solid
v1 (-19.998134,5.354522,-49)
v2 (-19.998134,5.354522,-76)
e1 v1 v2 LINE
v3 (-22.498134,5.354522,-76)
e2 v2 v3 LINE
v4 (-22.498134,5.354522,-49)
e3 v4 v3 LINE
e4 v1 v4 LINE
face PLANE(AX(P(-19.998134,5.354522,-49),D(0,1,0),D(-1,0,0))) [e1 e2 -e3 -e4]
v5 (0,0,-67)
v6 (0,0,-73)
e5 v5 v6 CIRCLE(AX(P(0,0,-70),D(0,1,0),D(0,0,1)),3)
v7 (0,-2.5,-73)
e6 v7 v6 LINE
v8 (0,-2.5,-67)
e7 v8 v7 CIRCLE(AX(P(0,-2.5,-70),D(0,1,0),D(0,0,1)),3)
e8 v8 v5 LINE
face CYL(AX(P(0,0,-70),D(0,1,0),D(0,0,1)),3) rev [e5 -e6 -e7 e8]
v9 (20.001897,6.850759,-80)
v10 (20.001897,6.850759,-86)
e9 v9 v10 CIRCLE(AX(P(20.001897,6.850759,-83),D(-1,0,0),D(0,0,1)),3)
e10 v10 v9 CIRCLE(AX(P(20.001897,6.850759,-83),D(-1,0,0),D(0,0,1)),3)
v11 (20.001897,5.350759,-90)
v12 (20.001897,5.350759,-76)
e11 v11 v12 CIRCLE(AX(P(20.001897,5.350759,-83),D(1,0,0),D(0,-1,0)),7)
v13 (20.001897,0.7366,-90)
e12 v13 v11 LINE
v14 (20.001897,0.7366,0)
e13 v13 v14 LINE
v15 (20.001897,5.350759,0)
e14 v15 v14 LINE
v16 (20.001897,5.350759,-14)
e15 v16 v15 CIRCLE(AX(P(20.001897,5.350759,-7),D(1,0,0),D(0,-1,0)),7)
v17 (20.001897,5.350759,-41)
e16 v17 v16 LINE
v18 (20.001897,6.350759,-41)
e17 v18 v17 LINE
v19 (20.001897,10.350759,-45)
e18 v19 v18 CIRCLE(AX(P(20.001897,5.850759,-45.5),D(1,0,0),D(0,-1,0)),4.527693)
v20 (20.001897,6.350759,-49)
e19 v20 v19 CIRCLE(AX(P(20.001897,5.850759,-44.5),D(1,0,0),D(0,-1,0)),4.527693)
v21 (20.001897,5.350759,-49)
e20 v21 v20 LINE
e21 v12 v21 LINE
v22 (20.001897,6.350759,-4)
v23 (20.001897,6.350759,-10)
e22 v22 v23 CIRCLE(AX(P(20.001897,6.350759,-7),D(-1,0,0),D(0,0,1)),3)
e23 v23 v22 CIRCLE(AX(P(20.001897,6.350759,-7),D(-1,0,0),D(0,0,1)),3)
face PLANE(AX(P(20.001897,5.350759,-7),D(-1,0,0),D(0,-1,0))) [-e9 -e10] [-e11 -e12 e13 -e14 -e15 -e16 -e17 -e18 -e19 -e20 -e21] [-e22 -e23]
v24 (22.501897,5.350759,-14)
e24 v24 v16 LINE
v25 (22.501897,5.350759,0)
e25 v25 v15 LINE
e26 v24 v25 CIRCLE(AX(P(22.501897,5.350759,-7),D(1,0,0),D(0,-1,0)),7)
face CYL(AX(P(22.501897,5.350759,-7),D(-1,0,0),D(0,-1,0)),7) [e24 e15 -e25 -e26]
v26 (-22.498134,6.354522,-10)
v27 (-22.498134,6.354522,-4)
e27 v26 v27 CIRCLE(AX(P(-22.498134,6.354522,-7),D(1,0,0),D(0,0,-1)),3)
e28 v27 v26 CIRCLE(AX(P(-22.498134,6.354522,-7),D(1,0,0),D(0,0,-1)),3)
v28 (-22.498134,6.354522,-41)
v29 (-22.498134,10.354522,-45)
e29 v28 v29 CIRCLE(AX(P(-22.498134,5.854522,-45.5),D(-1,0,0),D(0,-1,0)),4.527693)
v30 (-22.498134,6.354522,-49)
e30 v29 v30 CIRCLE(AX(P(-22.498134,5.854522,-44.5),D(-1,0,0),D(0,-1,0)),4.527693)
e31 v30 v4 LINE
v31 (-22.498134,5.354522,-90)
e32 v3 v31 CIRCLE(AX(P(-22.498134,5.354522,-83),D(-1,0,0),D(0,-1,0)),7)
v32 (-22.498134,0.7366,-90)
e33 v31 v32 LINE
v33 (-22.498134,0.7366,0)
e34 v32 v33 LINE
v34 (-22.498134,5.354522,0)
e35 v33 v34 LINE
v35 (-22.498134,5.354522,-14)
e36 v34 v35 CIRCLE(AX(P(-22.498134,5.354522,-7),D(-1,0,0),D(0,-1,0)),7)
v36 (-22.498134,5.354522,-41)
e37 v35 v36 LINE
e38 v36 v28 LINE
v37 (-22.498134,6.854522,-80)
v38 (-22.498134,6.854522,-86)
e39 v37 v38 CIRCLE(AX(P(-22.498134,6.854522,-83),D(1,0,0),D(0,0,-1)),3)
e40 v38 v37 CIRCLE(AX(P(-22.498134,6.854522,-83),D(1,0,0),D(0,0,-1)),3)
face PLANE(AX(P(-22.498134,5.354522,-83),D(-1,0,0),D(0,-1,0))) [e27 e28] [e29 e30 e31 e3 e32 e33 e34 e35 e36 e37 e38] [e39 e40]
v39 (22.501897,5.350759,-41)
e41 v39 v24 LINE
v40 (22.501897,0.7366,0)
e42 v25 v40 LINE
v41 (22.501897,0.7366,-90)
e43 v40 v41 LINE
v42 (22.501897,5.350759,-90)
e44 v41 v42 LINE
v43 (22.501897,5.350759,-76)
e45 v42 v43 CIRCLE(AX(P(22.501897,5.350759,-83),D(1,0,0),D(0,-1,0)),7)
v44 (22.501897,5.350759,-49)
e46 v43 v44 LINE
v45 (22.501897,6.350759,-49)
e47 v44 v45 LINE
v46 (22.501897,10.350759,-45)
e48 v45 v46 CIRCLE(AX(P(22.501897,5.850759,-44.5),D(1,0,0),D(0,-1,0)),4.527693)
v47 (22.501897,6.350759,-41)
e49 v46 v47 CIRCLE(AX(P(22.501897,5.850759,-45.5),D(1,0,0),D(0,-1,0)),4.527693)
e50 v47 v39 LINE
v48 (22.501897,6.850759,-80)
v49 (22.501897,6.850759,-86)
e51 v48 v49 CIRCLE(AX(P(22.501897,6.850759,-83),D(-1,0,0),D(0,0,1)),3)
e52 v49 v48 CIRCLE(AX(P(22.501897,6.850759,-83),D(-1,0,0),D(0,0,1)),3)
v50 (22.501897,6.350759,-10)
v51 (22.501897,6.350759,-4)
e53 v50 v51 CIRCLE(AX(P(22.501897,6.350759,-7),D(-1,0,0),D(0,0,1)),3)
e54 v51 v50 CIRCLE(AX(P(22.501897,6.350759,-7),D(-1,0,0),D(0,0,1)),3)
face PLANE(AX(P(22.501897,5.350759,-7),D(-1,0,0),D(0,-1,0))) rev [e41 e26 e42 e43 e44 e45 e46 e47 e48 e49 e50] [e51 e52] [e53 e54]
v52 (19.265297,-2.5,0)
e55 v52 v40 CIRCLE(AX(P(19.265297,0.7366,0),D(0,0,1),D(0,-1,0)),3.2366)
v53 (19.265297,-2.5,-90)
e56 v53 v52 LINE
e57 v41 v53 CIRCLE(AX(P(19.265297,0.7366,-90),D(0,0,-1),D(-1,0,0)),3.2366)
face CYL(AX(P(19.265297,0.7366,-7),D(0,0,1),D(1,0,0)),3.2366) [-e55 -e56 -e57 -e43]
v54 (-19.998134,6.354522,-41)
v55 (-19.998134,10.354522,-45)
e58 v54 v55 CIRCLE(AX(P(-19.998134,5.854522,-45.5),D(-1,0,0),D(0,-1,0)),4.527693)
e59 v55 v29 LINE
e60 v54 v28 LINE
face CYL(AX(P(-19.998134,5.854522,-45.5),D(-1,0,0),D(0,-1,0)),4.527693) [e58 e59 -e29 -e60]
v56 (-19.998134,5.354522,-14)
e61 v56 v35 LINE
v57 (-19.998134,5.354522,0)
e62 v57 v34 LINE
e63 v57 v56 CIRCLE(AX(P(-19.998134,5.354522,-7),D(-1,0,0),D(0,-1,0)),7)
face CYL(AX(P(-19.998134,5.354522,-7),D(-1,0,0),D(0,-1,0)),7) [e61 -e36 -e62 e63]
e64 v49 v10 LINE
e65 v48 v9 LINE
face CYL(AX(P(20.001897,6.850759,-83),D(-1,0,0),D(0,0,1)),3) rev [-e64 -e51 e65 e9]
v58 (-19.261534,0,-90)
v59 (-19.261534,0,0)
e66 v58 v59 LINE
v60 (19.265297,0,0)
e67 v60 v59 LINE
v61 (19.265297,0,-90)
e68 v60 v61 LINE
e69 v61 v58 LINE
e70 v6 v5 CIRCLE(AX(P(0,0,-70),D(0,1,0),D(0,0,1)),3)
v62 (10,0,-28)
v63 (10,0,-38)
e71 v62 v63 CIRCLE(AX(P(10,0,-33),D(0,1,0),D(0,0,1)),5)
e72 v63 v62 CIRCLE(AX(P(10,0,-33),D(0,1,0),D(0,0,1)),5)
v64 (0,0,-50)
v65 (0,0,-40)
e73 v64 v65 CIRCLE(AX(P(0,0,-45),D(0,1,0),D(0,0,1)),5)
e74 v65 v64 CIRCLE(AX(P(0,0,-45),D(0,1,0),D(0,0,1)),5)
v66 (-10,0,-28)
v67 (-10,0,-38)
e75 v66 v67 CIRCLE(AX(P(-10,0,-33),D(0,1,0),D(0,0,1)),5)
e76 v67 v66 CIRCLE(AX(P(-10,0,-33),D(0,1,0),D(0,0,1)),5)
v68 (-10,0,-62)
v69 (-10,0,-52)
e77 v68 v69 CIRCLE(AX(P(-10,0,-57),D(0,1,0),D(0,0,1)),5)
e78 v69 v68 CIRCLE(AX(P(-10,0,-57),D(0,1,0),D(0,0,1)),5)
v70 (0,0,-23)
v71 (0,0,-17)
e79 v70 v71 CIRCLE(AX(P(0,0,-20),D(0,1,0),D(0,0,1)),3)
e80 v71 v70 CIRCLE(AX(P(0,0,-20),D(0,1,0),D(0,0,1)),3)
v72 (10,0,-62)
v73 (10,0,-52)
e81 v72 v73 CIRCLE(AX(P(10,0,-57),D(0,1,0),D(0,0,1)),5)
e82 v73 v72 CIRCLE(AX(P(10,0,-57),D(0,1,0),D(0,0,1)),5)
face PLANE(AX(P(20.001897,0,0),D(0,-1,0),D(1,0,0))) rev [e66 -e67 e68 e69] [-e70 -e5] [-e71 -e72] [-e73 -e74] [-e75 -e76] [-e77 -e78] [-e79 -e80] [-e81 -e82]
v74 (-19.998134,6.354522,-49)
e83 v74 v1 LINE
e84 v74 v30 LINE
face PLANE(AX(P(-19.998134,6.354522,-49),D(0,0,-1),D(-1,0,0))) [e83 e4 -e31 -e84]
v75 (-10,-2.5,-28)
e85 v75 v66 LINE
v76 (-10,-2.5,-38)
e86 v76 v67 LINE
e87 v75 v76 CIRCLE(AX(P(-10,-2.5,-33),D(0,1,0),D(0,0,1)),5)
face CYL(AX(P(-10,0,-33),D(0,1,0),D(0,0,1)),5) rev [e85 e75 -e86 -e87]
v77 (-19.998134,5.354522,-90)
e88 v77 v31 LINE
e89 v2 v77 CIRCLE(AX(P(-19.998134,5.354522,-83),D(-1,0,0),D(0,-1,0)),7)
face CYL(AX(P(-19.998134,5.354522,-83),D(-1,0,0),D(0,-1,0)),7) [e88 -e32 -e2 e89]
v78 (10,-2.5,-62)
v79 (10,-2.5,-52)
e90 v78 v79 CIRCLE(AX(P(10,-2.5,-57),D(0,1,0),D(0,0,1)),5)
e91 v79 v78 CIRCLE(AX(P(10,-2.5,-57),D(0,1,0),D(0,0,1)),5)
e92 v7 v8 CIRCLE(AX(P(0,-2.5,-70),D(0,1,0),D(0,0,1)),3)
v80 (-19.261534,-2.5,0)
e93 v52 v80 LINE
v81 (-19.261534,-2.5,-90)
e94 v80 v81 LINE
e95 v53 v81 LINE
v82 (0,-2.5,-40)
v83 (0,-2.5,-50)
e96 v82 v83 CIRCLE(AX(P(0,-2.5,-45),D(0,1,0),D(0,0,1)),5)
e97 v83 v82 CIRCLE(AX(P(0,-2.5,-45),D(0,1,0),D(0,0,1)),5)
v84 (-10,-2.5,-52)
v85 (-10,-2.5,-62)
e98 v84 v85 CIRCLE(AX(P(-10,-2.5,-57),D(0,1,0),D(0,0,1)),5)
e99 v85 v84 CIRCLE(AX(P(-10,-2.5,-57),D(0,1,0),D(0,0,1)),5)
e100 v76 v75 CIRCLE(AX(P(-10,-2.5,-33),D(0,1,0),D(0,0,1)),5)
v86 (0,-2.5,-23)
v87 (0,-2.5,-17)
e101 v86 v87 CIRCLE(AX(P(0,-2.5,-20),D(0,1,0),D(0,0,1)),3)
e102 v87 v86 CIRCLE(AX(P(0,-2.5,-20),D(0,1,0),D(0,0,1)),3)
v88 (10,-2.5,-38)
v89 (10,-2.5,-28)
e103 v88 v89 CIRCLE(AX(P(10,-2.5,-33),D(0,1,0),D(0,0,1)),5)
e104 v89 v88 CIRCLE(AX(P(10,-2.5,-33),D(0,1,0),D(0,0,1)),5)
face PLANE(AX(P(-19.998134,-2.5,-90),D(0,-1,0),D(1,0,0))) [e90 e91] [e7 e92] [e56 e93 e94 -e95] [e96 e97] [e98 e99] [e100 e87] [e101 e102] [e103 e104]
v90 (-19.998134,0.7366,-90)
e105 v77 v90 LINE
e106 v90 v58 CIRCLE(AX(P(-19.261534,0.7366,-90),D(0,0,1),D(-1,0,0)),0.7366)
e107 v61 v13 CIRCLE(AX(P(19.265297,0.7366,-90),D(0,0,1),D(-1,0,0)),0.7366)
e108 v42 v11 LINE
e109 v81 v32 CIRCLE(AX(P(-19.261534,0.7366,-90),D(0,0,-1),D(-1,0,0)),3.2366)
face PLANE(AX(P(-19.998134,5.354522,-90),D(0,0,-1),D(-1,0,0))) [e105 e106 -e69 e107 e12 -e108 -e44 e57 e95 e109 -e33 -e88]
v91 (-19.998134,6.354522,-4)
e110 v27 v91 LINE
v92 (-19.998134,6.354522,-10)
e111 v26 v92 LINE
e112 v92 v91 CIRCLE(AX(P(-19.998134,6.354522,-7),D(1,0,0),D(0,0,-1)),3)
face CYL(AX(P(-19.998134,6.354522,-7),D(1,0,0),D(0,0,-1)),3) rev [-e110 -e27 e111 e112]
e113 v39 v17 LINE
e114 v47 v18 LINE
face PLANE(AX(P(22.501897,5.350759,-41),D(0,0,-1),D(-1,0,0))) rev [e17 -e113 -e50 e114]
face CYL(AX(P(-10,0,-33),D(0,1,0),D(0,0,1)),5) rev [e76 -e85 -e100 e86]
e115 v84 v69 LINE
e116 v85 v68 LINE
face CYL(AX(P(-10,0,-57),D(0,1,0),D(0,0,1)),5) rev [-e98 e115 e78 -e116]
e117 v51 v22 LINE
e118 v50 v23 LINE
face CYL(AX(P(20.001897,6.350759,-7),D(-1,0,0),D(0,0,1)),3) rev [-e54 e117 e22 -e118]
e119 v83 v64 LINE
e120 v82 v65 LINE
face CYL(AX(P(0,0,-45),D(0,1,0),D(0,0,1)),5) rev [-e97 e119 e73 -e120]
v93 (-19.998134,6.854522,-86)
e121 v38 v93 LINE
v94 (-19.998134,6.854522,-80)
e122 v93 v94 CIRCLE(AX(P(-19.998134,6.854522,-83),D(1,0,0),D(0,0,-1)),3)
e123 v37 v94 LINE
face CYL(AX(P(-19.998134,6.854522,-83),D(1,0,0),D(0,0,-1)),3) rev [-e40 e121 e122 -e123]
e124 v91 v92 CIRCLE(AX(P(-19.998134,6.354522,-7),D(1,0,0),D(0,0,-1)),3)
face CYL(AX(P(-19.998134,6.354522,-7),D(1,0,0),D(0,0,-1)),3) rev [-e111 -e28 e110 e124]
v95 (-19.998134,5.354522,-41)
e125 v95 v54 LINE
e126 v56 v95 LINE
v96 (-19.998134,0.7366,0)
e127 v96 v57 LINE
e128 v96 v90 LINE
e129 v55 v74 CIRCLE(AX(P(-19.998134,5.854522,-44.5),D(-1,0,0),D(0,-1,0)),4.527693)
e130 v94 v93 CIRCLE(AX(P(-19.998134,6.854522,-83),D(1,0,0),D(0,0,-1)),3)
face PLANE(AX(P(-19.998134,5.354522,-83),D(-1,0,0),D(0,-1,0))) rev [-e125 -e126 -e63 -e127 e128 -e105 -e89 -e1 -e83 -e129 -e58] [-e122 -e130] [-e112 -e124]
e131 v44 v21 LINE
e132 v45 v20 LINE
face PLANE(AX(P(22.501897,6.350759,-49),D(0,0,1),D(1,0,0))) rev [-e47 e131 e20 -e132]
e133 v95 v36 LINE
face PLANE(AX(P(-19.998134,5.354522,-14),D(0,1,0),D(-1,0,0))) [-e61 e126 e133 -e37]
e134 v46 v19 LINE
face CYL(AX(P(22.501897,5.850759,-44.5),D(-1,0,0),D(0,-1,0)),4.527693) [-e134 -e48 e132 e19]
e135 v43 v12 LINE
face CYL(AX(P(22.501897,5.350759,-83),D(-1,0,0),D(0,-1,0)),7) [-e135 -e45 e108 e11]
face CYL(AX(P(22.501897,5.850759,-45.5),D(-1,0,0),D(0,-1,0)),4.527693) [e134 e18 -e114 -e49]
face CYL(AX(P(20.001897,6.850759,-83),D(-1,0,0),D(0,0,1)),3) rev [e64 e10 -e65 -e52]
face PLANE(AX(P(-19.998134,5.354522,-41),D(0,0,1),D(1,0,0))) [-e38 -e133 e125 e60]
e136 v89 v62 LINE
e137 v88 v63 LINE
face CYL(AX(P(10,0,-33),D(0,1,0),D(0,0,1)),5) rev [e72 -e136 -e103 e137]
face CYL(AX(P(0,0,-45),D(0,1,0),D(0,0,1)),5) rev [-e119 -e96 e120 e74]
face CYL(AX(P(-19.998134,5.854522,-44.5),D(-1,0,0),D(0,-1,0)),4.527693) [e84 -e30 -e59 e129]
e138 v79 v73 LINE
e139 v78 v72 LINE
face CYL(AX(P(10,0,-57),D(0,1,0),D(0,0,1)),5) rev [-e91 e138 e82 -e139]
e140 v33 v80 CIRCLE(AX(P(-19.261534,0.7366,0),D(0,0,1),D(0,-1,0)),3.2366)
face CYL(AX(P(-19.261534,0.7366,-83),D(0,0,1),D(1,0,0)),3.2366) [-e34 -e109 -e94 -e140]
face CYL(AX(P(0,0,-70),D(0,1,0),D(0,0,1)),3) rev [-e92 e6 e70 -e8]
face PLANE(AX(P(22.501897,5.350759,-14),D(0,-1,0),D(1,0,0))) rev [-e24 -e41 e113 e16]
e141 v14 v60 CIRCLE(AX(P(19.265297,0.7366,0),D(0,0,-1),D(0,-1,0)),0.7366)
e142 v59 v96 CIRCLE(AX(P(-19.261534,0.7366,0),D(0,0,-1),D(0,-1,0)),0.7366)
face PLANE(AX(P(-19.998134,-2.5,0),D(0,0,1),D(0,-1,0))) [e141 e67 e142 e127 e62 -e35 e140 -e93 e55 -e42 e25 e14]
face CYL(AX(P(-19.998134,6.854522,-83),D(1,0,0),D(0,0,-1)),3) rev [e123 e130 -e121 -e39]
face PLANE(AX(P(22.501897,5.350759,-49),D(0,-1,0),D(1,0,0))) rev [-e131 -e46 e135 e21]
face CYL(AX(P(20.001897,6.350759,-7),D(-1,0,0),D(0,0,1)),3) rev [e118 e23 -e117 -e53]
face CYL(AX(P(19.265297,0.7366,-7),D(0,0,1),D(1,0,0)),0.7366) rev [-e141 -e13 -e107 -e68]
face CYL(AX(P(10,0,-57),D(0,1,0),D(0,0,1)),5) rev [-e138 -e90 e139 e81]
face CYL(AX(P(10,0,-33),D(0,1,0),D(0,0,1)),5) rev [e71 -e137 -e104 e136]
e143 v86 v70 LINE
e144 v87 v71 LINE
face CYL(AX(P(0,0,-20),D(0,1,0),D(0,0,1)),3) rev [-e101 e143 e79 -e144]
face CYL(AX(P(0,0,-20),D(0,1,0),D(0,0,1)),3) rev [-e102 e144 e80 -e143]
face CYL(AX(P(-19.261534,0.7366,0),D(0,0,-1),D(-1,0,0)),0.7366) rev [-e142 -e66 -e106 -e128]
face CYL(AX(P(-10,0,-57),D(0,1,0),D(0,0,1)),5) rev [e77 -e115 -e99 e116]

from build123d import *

# Parameters (mm, degrees)
BOSS_EXTRUDE1_DEPTH          = 2.5
SKETCH2_W                    = 90
SKETCH2_H                    = 2.5
BOSS_EXTRUDE2_DEPTH          = 40.000031182
BOSS_EXTRUDE3_DEPTH          = 2.5
F_6_0_6_DIAMETER_HOLE1_D     = 6
F_6_0_6_DIAMETER_HOLE1_DEPTH = 2.5
F_6_0_6_DIAMETER_HOLE2_D     = 6
F_6_0_6_DIAMETER_HOLE2_DEPTH = 2.5
F_10_0_10_DIAMETER_HOLE1_D   = 10
F_6_0_6_DIAMETER_HOLE3_D     = 6
FILLET1_R                    = 0.7366
FILLET2_R                    = 3.2366


with BuildPart() as part:
    # Sketch1 → Boss-Extrude1 (new body)
    with BuildSketch(Plane(origin=(-22.498134156, 0, 0), x_dir=(0, -1, 0), z_dir=(-1, 0, 0))):
        with BuildLine():
            Line((-5.354521861, -90), (2.5, -90))
            Line((2.5, -90), (2.5, 0))
            Line((2.5, 0), (-5.354521861, 0))
            ThreePointArc((-5.354521861, 0), (-12.354521861, -7), (-5.354521861, -14))
            Line((-5.354521861, -14), (-5.354521861, -41))
            Line((-5.354521861, -41), (-6.354521861, -41))
            ThreePointArc((-6.354521861, -41), (-9.05608398, -42.298437881), (-10.354521861, -45))
            ThreePointArc((-10.354521861, -45), (-9.05608398, -47.701562119), (-6.354521861, -49))
            Line((-6.354521861, -49), (-5.354521861, -49))
            Line((-5.354521861, -49), (-5.354521861, -76))
            ThreePointArc((-5.354521861, -76), (-12.354521861, -83), (-5.354521861, -90))
        make_face()
    extrude(amount=-BOSS_EXTRUDE1_DEPTH)

    # Sketch2 → Boss-Extrude2 (add)
    with BuildSketch(Plane(origin=(-19.998134156, 0, 0), x_dir=(0, 0, -1), z_dir=(1, 0, 0))):
        with Locations((45, -1.25)):
            Rectangle(SKETCH2_W, SKETCH2_H)
    extrude(amount=BOSS_EXTRUDE2_DEPTH)

    # Sketch3 → Boss-Extrude3 (add)
    with BuildSketch(Plane(origin=(20.001897026, 0, 0), x_dir=(0, 0, -1), z_dir=(1, 0, 0))):
        with BuildLine():
            Line((0, -2.5), (0, 5.350758991))
            ThreePointArc((0, 5.350758991), (7, 12.350758991), (14, 5.350758991))
            Line((14, 5.350758991), (41, 5.350758991))
            Line((41, 5.350758991), (41, 6.350758991))
            ThreePointArc((41, 6.350758991), (42.298437881, 9.05232111), (45, 10.350758991))
            ThreePointArc((45, 10.350758991), (47.701562119, 9.05232111), (49, 6.350758991))
            Line((49, 6.350758991), (49, 5.350758991))
            Line((49, 5.350758991), (76, 5.350758991))
            ThreePointArc((76, 5.350758991), (83, 12.350758991), (90, 5.350758991))
            Line((90, 5.350758991), (90, -2.5))
            Line((90, -2.5), (0, -2.5))
        make_face()
    extrude(amount=BOSS_EXTRUDE3_DEPTH)

    # Ø6.0 (6) Diameter Hole1
    with Locations(Plane.ZY.offset(-20.001897026)):
        with Locations((-83, 6.850758991), (-7, 6.350758991)):
            Hole(F_6_0_6_DIAMETER_HOLE1_D / 2, depth=F_6_0_6_DIAMETER_HOLE1_DEPTH)

    # Ø6.0 (6) Diameter Hole2
    with Locations(Plane(origin=(-19.998134156, 0, 0), x_dir=(0, 0, -1), z_dir=(1, 0, 0))):
        with Locations((83, 6.854521861), (7, 6.354521861)):
            Hole(F_6_0_6_DIAMETER_HOLE2_D / 2, depth=F_6_0_6_DIAMETER_HOLE2_DEPTH)

    # Ø10.0 (10) Diameter Hole1 (through all)
    with Locations(Plane(origin=(0, 0, 0), x_dir=(1, 0, 0), z_dir=(0, 1, 0))):
        with Locations((0, 45), (-10, 57), (-10, 33), (10, 33), (10, 57)):
            Hole(F_10_0_10_DIAMETER_HOLE1_D / 2)

    # Ø6.0 (6) Diameter Hole3 (through all)
    with Locations(Plane(origin=(0, 0, 0), x_dir=(1, 0, 0), z_dir=(0, 1, 0))):
        with Locations((0, 70), (0, 20)):
            Hole(F_6_0_6_DIAMETER_HOLE3_D / 2)

    # Fillet1
    fillet1_edges = [part.edges().sort_by_distance(p)[0] for p in [
        (-19.998134156, 0, -45),
        (20.001897026, 0, -45),
    ]]
    fillet(fillet1_edges, radius=FILLET1_R)

    # Fillet2
    fillet2_edges = [part.edges().sort_by_distance(p)[0] for p in [
        (-22.498134156, -2.5, -45),
        (22.501897026, -2.5, -45),
    ]]
    fillet(fillet2_edges, radius=FILLET2_R)


solid = part.part
